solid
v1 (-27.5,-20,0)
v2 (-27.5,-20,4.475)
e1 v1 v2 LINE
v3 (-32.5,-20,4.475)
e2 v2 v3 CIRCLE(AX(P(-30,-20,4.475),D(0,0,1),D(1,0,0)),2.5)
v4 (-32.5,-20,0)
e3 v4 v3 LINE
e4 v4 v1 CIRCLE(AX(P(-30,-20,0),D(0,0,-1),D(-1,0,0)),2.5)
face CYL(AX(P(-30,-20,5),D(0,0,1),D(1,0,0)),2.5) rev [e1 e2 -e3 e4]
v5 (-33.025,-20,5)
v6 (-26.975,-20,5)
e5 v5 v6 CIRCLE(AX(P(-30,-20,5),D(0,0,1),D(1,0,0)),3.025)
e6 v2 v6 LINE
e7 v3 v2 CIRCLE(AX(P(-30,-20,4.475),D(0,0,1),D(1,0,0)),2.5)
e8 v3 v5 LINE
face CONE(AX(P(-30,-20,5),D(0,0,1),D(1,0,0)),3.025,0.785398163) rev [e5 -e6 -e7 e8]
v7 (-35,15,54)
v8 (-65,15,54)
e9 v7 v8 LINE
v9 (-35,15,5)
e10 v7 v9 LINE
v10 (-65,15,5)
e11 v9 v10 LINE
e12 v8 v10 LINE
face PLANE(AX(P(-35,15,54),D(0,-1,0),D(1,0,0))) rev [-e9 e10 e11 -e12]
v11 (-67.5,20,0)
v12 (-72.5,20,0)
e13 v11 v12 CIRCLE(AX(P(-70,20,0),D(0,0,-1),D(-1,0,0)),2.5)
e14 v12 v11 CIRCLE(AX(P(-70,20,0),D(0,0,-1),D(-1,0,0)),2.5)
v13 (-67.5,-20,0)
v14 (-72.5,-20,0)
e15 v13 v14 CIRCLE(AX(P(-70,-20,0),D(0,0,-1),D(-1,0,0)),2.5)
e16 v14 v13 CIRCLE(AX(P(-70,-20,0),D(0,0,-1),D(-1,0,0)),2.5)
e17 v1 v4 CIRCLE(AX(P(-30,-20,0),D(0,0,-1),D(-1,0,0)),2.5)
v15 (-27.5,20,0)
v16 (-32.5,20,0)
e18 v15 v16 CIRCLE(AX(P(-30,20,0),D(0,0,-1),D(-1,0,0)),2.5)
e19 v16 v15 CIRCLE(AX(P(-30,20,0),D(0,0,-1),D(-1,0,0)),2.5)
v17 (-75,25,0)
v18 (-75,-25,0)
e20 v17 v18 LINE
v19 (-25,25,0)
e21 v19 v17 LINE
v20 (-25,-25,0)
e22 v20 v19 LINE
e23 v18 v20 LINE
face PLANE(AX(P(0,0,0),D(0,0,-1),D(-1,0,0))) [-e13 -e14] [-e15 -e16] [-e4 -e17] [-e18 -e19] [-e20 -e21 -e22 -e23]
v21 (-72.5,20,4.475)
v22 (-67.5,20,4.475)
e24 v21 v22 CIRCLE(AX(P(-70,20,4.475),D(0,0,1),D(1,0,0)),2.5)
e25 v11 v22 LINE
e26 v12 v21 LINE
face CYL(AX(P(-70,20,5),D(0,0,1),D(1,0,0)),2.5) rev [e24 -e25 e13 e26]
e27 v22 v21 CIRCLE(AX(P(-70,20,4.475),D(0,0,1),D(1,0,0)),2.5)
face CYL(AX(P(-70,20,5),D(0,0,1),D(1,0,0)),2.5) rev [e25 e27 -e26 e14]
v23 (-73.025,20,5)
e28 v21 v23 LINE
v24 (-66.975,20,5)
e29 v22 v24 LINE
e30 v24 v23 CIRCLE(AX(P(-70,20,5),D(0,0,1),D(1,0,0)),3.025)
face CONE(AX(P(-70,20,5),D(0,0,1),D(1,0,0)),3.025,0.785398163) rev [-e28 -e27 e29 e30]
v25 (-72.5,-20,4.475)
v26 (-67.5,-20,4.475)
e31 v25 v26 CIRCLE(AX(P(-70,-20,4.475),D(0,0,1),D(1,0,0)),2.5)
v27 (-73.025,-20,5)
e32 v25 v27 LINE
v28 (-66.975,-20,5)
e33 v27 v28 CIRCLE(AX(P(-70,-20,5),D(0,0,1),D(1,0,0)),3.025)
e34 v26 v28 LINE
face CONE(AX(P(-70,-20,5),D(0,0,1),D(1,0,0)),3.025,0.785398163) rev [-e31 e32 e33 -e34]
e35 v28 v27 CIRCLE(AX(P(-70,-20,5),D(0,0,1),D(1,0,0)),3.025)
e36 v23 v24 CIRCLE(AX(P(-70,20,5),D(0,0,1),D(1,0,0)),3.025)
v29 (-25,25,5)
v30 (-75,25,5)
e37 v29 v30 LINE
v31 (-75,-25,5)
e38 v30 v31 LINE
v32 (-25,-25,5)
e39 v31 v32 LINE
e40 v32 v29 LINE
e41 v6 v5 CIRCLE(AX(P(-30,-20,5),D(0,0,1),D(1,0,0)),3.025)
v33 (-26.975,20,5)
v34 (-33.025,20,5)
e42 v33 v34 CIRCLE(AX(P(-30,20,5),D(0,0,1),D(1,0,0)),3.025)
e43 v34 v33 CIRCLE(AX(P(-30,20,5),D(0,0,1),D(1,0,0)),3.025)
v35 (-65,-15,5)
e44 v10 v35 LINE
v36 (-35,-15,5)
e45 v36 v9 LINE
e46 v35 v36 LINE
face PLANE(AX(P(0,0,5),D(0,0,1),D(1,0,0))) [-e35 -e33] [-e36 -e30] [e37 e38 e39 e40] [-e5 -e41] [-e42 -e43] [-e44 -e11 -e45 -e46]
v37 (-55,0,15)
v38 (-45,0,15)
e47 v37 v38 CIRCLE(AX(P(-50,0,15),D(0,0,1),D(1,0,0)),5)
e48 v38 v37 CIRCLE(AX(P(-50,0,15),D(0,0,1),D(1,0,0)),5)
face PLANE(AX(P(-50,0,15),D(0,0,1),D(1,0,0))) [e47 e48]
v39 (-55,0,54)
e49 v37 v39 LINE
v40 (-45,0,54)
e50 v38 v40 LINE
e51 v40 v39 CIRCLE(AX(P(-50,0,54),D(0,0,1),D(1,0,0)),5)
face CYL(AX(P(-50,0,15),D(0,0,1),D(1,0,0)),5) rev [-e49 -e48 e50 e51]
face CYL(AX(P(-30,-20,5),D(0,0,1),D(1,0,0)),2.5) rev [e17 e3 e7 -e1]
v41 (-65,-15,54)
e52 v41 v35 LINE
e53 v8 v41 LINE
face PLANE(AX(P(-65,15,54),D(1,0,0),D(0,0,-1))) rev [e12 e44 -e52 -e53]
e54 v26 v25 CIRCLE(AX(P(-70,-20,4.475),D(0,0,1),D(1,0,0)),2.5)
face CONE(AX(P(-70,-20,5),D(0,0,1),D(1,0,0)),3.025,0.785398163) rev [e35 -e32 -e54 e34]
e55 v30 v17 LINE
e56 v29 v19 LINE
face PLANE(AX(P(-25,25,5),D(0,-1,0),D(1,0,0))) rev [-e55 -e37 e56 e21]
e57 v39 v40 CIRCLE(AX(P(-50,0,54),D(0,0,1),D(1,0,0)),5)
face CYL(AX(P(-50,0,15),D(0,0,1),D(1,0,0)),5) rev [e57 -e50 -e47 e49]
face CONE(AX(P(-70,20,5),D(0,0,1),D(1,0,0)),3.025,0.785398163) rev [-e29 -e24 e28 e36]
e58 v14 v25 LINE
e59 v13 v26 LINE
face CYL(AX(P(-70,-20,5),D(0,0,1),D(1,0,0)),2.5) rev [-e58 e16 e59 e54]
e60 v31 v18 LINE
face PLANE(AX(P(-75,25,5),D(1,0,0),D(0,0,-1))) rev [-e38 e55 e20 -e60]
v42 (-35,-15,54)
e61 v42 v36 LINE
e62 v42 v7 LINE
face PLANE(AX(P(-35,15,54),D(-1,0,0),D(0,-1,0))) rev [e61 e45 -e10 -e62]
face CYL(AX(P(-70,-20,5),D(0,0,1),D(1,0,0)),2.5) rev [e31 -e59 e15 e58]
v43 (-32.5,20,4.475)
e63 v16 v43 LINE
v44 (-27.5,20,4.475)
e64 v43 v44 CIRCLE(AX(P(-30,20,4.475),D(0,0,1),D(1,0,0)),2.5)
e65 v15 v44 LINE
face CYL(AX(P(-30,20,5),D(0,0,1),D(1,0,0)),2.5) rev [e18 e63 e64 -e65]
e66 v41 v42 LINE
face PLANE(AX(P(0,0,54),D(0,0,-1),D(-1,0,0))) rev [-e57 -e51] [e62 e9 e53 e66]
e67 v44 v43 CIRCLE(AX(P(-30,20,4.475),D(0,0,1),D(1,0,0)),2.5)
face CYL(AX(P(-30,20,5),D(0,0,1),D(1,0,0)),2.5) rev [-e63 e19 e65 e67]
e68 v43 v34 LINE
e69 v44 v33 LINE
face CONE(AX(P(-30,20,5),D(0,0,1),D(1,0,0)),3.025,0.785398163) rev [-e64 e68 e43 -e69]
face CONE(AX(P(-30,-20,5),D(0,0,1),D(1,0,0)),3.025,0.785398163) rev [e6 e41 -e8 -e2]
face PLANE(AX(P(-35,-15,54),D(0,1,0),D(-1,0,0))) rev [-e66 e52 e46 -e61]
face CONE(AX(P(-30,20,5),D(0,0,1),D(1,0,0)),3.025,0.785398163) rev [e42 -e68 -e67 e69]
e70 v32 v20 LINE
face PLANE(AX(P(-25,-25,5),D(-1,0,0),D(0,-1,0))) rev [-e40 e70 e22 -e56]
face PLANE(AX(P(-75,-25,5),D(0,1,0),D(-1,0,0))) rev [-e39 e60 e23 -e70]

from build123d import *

# Parameters (mm, degrees)
SKETCH_1_W                   = 30
SKETCH_1_H                   = 30
EXTRUDE_1_DEPTH              = 54
SKETCH_2_W                   = 50
SKETCH_2_H                   = 50
EXTRUDE_2_DEPTH              = 5
HOLE_WIZARD_M6_1_D           = 5
HOLE_WIZARD_M6_1_DEPTH       = 13.497848452
HOLE_WIZARD_M6_1_CSINK_D     = 6.05
HOLE_WIZARD_M6_1_CSINK_ANGLE = 90
HOLE_WIZARD_M6_1_TIP         = 1.502151548
SKETCH_6_R                   = 5
CUT_EXTRUDE_1_DEPTH          = 39


with BuildPart() as part:
    # 草图1 → 凸台-拉伸1 (new body)
    with BuildSketch(Plane.XY):
        with Locations((-50, 0)):
            Rectangle(SKETCH_1_W, SKETCH_1_H)
    extrude(amount=EXTRUDE_1_DEPTH)

    # 草图2 → 凸台-拉伸2 (add)
    with BuildSketch(Plane.XY):
        with Locations((-50, 0)):
            Rectangle(SKETCH_2_W, SKETCH_2_H)
    extrude(amount=EXTRUDE_2_DEPTH)

    # M6 螺纹孔1
    with Locations(Plane.XY.offset(5)):
        with Locations((-30, 20), (-70, 20), (-70, -20), (-30, -20)):
            CounterSinkHole(HOLE_WIZARD_M6_1_D / 2, HOLE_WIZARD_M6_1_CSINK_D / 2, depth=HOLE_WIZARD_M6_1_DEPTH, counter_sink_angle=HOLE_WIZARD_M6_1_CSINK_ANGLE)
            with Locations((0, 0, -(HOLE_WIZARD_M6_1_DEPTH + HOLE_WIZARD_M6_1_TIP / 2))):  # 118° drill point
                Cone(0, HOLE_WIZARD_M6_1_D / 2, HOLE_WIZARD_M6_1_TIP, mode=Mode.SUBTRACT)

    # 草图6 → 切除-拉伸1 (cut)
    with BuildSketch(Plane.XY.offset(54)):
        with Locations((-50, 0)):
            Circle(SKETCH_6_R)
    extrude(amount=-CUT_EXTRUDE_1_DEPTH, mode=Mode.SUBTRACT)


solid = part.part
